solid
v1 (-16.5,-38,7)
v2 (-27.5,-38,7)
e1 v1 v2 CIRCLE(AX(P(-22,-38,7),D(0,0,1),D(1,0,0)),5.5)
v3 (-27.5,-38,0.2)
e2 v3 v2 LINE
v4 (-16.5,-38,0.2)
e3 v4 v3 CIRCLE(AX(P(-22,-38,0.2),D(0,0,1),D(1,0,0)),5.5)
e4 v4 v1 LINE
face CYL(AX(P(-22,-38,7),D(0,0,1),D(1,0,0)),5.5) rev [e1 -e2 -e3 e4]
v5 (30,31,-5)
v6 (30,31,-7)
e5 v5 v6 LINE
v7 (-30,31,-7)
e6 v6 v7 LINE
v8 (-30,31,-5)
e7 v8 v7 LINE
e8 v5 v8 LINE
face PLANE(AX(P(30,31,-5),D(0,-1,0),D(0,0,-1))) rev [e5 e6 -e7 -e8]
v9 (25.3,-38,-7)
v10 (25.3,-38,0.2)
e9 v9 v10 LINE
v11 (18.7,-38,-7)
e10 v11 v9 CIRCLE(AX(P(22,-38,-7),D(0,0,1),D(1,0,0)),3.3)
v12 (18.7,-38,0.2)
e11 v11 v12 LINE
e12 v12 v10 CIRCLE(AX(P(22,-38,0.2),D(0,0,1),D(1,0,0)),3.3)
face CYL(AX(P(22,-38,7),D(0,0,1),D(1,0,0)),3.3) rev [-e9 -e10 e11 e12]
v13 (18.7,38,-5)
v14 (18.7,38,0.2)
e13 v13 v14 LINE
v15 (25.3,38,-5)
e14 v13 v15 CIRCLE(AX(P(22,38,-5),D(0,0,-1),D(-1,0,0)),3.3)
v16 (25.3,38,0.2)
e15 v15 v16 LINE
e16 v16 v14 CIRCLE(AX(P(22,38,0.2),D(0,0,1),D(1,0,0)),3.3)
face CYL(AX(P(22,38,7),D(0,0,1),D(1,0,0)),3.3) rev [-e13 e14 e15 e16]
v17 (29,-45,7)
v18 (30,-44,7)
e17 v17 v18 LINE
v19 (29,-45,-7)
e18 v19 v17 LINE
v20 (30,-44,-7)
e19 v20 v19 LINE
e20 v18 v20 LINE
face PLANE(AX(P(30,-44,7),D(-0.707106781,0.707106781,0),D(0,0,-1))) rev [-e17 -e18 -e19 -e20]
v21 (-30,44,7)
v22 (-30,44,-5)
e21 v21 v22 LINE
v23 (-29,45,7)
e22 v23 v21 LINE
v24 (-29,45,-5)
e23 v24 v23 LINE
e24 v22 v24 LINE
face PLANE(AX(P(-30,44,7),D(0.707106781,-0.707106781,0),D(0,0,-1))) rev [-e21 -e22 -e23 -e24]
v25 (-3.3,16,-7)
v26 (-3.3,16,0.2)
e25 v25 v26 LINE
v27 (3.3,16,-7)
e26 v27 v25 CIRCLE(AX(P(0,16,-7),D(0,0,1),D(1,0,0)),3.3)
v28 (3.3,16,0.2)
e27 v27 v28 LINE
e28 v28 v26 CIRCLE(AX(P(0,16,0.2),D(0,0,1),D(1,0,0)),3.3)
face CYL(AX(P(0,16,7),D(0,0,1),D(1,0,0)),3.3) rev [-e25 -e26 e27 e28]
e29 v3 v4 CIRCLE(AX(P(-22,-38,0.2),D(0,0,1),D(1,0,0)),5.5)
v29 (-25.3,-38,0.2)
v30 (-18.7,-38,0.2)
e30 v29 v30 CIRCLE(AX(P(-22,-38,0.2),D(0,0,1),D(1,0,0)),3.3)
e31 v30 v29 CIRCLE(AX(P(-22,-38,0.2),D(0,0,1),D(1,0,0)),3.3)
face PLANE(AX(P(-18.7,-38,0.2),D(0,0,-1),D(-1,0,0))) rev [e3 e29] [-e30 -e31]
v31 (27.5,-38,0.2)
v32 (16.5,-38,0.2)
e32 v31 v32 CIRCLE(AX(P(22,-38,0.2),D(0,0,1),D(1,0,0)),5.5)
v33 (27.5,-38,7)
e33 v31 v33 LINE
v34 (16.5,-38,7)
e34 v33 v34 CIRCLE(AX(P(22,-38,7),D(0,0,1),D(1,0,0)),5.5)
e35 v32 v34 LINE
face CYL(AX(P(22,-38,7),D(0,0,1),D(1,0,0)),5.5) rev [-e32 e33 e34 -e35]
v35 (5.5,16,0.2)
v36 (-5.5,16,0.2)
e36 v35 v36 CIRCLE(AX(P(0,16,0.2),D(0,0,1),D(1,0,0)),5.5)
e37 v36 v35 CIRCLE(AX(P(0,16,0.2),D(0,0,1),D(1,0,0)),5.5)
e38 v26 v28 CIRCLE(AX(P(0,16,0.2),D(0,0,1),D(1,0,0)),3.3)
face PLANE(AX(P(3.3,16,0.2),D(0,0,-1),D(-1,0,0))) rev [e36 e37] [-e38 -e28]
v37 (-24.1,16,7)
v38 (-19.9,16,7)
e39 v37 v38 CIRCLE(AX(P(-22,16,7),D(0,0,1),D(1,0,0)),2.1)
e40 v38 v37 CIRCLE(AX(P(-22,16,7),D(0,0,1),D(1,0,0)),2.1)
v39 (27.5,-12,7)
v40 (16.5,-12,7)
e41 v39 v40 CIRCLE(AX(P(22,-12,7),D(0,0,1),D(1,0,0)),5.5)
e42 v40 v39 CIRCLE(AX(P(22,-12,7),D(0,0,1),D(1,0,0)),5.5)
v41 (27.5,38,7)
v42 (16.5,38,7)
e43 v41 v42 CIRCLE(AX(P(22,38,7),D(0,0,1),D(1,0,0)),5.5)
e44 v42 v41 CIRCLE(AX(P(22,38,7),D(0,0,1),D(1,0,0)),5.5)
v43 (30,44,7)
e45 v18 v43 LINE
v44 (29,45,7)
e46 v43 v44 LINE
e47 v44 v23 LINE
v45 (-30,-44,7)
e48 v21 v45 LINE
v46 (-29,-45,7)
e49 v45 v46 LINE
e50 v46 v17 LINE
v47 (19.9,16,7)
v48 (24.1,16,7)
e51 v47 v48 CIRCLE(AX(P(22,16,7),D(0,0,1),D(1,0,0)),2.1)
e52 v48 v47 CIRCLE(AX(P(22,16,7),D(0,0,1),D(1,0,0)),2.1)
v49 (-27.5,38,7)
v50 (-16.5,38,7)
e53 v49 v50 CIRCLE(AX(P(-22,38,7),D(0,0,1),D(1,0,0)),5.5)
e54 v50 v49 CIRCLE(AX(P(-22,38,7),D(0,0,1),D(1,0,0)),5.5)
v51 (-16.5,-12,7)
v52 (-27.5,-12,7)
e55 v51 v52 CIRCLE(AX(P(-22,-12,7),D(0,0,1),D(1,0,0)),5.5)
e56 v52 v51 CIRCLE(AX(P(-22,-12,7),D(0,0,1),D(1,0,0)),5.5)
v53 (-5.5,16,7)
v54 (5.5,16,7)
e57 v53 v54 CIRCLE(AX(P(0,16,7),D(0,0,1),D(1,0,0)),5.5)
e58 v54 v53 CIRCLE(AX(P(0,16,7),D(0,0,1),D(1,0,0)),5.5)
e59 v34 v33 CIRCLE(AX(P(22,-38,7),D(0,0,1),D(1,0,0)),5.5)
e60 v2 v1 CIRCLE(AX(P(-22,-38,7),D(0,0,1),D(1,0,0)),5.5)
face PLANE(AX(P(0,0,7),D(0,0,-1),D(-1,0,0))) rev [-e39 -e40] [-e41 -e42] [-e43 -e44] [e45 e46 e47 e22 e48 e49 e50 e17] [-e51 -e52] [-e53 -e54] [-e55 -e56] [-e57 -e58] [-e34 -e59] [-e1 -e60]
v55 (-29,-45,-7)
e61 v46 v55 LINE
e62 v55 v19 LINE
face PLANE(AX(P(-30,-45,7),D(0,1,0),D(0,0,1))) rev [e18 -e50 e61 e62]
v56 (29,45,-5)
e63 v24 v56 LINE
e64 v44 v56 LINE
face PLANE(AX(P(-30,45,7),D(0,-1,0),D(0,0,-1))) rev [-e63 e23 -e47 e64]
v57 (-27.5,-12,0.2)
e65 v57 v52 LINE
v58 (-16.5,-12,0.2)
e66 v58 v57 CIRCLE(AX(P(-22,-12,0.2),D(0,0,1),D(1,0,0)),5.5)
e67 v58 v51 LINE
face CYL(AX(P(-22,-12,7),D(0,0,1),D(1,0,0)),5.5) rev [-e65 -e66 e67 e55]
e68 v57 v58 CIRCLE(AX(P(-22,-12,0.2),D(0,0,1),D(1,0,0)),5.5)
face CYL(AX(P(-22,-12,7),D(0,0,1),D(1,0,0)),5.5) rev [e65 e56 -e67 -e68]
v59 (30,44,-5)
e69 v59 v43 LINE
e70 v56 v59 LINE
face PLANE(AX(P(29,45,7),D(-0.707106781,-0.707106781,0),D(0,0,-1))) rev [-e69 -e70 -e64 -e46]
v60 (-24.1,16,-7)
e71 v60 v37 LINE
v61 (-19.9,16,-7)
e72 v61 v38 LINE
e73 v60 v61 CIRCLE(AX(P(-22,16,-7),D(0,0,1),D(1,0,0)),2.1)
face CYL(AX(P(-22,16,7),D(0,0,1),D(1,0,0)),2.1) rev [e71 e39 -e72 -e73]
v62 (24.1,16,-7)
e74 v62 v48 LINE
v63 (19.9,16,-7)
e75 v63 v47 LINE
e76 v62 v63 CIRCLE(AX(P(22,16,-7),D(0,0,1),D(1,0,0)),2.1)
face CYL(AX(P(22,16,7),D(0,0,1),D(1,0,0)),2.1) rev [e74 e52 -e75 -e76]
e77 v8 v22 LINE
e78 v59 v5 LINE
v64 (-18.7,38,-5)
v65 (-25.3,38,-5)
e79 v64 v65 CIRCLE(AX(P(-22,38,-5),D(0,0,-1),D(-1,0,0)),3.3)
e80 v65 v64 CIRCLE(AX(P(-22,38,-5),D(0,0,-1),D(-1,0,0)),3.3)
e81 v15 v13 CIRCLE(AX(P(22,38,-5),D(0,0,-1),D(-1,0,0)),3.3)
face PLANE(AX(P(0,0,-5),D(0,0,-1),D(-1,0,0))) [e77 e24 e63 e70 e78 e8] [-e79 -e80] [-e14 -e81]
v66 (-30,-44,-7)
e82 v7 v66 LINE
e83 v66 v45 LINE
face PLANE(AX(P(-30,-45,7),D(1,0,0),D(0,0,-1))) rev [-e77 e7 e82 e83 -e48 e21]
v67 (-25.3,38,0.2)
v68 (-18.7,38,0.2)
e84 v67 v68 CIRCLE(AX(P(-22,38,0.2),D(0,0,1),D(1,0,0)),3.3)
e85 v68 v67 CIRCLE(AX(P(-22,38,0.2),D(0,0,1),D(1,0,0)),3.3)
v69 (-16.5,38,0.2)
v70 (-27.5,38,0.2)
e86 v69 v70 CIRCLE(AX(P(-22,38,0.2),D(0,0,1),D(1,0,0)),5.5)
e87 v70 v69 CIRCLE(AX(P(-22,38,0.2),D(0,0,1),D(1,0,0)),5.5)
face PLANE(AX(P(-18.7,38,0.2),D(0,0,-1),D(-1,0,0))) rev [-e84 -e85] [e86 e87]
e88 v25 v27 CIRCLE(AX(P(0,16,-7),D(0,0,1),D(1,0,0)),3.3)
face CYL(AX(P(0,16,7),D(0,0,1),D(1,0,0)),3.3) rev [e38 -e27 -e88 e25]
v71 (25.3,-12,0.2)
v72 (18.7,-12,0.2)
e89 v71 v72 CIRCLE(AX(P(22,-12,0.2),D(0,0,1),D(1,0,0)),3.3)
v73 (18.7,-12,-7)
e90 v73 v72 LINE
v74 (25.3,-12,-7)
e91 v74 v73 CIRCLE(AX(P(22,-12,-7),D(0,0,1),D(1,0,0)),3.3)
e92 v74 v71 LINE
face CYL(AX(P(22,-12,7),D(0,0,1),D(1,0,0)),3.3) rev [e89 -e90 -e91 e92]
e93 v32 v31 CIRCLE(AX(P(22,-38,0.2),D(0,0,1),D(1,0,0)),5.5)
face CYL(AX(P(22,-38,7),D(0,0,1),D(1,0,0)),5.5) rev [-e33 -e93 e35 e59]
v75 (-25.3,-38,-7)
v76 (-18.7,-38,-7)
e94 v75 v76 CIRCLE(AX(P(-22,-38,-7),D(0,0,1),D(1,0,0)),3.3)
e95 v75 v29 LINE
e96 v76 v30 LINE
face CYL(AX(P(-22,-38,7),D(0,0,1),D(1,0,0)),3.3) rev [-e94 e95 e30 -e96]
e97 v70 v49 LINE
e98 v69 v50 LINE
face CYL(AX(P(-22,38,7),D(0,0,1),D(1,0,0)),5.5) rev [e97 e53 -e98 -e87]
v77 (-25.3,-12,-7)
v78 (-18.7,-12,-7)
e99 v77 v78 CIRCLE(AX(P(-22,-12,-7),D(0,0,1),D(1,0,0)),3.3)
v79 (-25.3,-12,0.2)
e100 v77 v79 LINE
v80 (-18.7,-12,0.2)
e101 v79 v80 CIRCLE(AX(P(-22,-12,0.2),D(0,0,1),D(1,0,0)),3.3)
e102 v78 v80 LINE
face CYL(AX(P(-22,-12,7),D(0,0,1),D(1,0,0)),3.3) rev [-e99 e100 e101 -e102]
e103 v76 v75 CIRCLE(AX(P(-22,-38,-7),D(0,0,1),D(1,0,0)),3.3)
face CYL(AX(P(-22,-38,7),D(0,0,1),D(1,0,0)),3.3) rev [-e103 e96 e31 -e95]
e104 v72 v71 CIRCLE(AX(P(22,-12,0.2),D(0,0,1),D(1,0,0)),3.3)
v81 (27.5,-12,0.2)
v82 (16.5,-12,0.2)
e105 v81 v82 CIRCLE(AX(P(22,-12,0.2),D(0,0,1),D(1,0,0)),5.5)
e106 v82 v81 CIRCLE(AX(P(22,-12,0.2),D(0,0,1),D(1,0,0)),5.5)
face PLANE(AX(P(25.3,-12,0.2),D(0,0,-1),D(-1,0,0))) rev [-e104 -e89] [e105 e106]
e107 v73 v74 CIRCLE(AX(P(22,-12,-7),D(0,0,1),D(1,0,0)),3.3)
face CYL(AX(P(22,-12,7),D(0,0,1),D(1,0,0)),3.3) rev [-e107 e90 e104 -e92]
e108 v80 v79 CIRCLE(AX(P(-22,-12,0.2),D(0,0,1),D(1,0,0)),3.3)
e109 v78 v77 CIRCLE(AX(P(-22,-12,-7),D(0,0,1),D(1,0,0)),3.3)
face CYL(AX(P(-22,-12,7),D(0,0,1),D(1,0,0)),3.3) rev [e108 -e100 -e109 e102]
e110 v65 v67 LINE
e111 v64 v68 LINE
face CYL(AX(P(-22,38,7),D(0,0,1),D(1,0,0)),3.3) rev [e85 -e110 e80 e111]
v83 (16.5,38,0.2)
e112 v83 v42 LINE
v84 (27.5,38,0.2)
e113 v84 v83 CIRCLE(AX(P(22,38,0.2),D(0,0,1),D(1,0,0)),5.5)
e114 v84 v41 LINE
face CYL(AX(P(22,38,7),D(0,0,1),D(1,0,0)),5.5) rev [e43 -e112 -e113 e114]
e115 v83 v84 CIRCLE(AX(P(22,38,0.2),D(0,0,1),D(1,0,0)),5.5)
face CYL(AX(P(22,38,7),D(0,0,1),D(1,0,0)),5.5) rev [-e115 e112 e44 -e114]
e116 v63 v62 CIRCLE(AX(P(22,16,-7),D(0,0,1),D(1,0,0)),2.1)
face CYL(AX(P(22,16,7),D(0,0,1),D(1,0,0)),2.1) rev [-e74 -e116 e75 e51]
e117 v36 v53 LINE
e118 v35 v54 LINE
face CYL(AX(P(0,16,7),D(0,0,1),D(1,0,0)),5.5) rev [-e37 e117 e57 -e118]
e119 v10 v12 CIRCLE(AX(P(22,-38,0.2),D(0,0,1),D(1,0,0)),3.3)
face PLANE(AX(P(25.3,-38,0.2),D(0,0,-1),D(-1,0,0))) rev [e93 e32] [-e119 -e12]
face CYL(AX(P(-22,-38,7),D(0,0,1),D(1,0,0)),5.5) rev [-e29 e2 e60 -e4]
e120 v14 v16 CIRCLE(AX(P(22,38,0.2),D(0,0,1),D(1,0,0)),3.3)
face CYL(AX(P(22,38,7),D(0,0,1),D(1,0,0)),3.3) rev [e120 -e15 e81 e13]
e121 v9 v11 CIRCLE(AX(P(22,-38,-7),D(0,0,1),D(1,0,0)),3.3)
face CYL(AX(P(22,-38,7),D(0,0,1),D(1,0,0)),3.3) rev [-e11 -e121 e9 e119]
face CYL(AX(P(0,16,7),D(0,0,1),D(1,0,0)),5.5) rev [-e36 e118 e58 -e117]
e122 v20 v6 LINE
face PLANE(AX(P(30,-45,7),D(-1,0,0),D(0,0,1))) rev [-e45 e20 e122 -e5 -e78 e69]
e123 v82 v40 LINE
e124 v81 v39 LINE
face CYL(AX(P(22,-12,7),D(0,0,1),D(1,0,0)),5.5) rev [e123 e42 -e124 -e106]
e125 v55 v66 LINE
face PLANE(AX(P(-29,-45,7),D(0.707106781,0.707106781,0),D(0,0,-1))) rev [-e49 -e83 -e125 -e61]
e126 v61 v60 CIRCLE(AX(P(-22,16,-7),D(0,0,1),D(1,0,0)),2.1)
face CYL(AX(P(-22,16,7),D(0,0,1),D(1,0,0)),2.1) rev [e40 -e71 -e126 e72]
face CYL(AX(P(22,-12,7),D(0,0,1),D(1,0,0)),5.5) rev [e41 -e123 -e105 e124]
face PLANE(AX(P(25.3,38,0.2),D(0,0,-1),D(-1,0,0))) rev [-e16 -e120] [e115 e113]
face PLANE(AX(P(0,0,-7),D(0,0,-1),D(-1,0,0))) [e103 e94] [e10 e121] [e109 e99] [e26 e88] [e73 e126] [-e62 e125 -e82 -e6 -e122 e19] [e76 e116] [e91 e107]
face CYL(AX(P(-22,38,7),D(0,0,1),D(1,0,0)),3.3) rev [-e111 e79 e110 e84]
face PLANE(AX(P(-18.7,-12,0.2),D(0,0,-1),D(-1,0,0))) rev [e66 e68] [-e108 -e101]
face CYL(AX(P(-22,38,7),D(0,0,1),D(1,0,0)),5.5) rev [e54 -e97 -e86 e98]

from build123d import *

# Parameters (mm, degrees)
SKETCH1_W                                            = 60
SKETCH1_H                                            = 90
BOSS_EXTRUDE1_DEPTH                                  = 7
SKETCH2_W                                            = 60
SKETCH2_H                                            = 14
CUT_EXTRUDE1_DEPTH                                   = 2
HOLE_SIZE_PER_SOCKET_HEAD_CAP_SCREW_TYPE_D           = 6.6
HOLE_SIZE_PER_SOCKET_HEAD_CAP_SCREW_TYPE_CBORE_D     = 11
HOLE_SIZE_PER_SOCKET_HEAD_CAP_SCREW_TYPE_CBORE_DEPTH = 6.8
CHAMFER1_SIZE                                        = 1
M5_TAPPED_HOLE1_D                                    = 4.2


with BuildPart() as part:
    # Sketch1 → Boss-Extrude1 (new, symmetric)
    with BuildSketch(Plane.XY):
        Rectangle(SKETCH1_W, SKETCH1_H)
    extrude(amount=BOSS_EXTRUDE1_DEPTH, both=True)

    # Sketch2 → Cut-Extrude1 (cut)
    with BuildSketch(Plane(origin=(0, 0, -7), x_dir=(-1, 0, 0), z_dir=(0, 0, -1))):
        with Locations((0, 38)):
            Rectangle(SKETCH2_W, SKETCH2_H)
    extrude(amount=-CUT_EXTRUDE1_DEPTH, mode=Mode.SUBTRACT)

    # Hole Size per Socket Head Cap Screw Type1 (through all)
    with Locations(Plane.XY.offset(7)):
        with Locations((0, 16), (-22, 38), (22, 38), (-22, -12), (22, -38), (-22, -38), (22, -12)):
            CounterBoreHole(HOLE_SIZE_PER_SOCKET_HEAD_CAP_SCREW_TYPE_D / 2, HOLE_SIZE_PER_SOCKET_HEAD_CAP_SCREW_TYPE_CBORE_D / 2, HOLE_SIZE_PER_SOCKET_HEAD_CAP_SCREW_TYPE_CBORE_DEPTH)

    # Chamfer1
    chamfer1_edges = [part.edges().sort_by_distance(p)[0] for p in [
        (30, -45, 0),
        (-30, -45, 0),
        (-30, 45, 1),
        (30, 45, 1),
    ]]
    chamfer(chamfer1_edges, length=CHAMFER1_SIZE)

    # M5 Tapped Hole1 (through all)
    with Locations(Plane.XY.offset(7)):
        with Locations((22, 16), (-22, 16)):
            Hole(M5_TAPPED_HOLE1_D / 2)


solid = part.part
